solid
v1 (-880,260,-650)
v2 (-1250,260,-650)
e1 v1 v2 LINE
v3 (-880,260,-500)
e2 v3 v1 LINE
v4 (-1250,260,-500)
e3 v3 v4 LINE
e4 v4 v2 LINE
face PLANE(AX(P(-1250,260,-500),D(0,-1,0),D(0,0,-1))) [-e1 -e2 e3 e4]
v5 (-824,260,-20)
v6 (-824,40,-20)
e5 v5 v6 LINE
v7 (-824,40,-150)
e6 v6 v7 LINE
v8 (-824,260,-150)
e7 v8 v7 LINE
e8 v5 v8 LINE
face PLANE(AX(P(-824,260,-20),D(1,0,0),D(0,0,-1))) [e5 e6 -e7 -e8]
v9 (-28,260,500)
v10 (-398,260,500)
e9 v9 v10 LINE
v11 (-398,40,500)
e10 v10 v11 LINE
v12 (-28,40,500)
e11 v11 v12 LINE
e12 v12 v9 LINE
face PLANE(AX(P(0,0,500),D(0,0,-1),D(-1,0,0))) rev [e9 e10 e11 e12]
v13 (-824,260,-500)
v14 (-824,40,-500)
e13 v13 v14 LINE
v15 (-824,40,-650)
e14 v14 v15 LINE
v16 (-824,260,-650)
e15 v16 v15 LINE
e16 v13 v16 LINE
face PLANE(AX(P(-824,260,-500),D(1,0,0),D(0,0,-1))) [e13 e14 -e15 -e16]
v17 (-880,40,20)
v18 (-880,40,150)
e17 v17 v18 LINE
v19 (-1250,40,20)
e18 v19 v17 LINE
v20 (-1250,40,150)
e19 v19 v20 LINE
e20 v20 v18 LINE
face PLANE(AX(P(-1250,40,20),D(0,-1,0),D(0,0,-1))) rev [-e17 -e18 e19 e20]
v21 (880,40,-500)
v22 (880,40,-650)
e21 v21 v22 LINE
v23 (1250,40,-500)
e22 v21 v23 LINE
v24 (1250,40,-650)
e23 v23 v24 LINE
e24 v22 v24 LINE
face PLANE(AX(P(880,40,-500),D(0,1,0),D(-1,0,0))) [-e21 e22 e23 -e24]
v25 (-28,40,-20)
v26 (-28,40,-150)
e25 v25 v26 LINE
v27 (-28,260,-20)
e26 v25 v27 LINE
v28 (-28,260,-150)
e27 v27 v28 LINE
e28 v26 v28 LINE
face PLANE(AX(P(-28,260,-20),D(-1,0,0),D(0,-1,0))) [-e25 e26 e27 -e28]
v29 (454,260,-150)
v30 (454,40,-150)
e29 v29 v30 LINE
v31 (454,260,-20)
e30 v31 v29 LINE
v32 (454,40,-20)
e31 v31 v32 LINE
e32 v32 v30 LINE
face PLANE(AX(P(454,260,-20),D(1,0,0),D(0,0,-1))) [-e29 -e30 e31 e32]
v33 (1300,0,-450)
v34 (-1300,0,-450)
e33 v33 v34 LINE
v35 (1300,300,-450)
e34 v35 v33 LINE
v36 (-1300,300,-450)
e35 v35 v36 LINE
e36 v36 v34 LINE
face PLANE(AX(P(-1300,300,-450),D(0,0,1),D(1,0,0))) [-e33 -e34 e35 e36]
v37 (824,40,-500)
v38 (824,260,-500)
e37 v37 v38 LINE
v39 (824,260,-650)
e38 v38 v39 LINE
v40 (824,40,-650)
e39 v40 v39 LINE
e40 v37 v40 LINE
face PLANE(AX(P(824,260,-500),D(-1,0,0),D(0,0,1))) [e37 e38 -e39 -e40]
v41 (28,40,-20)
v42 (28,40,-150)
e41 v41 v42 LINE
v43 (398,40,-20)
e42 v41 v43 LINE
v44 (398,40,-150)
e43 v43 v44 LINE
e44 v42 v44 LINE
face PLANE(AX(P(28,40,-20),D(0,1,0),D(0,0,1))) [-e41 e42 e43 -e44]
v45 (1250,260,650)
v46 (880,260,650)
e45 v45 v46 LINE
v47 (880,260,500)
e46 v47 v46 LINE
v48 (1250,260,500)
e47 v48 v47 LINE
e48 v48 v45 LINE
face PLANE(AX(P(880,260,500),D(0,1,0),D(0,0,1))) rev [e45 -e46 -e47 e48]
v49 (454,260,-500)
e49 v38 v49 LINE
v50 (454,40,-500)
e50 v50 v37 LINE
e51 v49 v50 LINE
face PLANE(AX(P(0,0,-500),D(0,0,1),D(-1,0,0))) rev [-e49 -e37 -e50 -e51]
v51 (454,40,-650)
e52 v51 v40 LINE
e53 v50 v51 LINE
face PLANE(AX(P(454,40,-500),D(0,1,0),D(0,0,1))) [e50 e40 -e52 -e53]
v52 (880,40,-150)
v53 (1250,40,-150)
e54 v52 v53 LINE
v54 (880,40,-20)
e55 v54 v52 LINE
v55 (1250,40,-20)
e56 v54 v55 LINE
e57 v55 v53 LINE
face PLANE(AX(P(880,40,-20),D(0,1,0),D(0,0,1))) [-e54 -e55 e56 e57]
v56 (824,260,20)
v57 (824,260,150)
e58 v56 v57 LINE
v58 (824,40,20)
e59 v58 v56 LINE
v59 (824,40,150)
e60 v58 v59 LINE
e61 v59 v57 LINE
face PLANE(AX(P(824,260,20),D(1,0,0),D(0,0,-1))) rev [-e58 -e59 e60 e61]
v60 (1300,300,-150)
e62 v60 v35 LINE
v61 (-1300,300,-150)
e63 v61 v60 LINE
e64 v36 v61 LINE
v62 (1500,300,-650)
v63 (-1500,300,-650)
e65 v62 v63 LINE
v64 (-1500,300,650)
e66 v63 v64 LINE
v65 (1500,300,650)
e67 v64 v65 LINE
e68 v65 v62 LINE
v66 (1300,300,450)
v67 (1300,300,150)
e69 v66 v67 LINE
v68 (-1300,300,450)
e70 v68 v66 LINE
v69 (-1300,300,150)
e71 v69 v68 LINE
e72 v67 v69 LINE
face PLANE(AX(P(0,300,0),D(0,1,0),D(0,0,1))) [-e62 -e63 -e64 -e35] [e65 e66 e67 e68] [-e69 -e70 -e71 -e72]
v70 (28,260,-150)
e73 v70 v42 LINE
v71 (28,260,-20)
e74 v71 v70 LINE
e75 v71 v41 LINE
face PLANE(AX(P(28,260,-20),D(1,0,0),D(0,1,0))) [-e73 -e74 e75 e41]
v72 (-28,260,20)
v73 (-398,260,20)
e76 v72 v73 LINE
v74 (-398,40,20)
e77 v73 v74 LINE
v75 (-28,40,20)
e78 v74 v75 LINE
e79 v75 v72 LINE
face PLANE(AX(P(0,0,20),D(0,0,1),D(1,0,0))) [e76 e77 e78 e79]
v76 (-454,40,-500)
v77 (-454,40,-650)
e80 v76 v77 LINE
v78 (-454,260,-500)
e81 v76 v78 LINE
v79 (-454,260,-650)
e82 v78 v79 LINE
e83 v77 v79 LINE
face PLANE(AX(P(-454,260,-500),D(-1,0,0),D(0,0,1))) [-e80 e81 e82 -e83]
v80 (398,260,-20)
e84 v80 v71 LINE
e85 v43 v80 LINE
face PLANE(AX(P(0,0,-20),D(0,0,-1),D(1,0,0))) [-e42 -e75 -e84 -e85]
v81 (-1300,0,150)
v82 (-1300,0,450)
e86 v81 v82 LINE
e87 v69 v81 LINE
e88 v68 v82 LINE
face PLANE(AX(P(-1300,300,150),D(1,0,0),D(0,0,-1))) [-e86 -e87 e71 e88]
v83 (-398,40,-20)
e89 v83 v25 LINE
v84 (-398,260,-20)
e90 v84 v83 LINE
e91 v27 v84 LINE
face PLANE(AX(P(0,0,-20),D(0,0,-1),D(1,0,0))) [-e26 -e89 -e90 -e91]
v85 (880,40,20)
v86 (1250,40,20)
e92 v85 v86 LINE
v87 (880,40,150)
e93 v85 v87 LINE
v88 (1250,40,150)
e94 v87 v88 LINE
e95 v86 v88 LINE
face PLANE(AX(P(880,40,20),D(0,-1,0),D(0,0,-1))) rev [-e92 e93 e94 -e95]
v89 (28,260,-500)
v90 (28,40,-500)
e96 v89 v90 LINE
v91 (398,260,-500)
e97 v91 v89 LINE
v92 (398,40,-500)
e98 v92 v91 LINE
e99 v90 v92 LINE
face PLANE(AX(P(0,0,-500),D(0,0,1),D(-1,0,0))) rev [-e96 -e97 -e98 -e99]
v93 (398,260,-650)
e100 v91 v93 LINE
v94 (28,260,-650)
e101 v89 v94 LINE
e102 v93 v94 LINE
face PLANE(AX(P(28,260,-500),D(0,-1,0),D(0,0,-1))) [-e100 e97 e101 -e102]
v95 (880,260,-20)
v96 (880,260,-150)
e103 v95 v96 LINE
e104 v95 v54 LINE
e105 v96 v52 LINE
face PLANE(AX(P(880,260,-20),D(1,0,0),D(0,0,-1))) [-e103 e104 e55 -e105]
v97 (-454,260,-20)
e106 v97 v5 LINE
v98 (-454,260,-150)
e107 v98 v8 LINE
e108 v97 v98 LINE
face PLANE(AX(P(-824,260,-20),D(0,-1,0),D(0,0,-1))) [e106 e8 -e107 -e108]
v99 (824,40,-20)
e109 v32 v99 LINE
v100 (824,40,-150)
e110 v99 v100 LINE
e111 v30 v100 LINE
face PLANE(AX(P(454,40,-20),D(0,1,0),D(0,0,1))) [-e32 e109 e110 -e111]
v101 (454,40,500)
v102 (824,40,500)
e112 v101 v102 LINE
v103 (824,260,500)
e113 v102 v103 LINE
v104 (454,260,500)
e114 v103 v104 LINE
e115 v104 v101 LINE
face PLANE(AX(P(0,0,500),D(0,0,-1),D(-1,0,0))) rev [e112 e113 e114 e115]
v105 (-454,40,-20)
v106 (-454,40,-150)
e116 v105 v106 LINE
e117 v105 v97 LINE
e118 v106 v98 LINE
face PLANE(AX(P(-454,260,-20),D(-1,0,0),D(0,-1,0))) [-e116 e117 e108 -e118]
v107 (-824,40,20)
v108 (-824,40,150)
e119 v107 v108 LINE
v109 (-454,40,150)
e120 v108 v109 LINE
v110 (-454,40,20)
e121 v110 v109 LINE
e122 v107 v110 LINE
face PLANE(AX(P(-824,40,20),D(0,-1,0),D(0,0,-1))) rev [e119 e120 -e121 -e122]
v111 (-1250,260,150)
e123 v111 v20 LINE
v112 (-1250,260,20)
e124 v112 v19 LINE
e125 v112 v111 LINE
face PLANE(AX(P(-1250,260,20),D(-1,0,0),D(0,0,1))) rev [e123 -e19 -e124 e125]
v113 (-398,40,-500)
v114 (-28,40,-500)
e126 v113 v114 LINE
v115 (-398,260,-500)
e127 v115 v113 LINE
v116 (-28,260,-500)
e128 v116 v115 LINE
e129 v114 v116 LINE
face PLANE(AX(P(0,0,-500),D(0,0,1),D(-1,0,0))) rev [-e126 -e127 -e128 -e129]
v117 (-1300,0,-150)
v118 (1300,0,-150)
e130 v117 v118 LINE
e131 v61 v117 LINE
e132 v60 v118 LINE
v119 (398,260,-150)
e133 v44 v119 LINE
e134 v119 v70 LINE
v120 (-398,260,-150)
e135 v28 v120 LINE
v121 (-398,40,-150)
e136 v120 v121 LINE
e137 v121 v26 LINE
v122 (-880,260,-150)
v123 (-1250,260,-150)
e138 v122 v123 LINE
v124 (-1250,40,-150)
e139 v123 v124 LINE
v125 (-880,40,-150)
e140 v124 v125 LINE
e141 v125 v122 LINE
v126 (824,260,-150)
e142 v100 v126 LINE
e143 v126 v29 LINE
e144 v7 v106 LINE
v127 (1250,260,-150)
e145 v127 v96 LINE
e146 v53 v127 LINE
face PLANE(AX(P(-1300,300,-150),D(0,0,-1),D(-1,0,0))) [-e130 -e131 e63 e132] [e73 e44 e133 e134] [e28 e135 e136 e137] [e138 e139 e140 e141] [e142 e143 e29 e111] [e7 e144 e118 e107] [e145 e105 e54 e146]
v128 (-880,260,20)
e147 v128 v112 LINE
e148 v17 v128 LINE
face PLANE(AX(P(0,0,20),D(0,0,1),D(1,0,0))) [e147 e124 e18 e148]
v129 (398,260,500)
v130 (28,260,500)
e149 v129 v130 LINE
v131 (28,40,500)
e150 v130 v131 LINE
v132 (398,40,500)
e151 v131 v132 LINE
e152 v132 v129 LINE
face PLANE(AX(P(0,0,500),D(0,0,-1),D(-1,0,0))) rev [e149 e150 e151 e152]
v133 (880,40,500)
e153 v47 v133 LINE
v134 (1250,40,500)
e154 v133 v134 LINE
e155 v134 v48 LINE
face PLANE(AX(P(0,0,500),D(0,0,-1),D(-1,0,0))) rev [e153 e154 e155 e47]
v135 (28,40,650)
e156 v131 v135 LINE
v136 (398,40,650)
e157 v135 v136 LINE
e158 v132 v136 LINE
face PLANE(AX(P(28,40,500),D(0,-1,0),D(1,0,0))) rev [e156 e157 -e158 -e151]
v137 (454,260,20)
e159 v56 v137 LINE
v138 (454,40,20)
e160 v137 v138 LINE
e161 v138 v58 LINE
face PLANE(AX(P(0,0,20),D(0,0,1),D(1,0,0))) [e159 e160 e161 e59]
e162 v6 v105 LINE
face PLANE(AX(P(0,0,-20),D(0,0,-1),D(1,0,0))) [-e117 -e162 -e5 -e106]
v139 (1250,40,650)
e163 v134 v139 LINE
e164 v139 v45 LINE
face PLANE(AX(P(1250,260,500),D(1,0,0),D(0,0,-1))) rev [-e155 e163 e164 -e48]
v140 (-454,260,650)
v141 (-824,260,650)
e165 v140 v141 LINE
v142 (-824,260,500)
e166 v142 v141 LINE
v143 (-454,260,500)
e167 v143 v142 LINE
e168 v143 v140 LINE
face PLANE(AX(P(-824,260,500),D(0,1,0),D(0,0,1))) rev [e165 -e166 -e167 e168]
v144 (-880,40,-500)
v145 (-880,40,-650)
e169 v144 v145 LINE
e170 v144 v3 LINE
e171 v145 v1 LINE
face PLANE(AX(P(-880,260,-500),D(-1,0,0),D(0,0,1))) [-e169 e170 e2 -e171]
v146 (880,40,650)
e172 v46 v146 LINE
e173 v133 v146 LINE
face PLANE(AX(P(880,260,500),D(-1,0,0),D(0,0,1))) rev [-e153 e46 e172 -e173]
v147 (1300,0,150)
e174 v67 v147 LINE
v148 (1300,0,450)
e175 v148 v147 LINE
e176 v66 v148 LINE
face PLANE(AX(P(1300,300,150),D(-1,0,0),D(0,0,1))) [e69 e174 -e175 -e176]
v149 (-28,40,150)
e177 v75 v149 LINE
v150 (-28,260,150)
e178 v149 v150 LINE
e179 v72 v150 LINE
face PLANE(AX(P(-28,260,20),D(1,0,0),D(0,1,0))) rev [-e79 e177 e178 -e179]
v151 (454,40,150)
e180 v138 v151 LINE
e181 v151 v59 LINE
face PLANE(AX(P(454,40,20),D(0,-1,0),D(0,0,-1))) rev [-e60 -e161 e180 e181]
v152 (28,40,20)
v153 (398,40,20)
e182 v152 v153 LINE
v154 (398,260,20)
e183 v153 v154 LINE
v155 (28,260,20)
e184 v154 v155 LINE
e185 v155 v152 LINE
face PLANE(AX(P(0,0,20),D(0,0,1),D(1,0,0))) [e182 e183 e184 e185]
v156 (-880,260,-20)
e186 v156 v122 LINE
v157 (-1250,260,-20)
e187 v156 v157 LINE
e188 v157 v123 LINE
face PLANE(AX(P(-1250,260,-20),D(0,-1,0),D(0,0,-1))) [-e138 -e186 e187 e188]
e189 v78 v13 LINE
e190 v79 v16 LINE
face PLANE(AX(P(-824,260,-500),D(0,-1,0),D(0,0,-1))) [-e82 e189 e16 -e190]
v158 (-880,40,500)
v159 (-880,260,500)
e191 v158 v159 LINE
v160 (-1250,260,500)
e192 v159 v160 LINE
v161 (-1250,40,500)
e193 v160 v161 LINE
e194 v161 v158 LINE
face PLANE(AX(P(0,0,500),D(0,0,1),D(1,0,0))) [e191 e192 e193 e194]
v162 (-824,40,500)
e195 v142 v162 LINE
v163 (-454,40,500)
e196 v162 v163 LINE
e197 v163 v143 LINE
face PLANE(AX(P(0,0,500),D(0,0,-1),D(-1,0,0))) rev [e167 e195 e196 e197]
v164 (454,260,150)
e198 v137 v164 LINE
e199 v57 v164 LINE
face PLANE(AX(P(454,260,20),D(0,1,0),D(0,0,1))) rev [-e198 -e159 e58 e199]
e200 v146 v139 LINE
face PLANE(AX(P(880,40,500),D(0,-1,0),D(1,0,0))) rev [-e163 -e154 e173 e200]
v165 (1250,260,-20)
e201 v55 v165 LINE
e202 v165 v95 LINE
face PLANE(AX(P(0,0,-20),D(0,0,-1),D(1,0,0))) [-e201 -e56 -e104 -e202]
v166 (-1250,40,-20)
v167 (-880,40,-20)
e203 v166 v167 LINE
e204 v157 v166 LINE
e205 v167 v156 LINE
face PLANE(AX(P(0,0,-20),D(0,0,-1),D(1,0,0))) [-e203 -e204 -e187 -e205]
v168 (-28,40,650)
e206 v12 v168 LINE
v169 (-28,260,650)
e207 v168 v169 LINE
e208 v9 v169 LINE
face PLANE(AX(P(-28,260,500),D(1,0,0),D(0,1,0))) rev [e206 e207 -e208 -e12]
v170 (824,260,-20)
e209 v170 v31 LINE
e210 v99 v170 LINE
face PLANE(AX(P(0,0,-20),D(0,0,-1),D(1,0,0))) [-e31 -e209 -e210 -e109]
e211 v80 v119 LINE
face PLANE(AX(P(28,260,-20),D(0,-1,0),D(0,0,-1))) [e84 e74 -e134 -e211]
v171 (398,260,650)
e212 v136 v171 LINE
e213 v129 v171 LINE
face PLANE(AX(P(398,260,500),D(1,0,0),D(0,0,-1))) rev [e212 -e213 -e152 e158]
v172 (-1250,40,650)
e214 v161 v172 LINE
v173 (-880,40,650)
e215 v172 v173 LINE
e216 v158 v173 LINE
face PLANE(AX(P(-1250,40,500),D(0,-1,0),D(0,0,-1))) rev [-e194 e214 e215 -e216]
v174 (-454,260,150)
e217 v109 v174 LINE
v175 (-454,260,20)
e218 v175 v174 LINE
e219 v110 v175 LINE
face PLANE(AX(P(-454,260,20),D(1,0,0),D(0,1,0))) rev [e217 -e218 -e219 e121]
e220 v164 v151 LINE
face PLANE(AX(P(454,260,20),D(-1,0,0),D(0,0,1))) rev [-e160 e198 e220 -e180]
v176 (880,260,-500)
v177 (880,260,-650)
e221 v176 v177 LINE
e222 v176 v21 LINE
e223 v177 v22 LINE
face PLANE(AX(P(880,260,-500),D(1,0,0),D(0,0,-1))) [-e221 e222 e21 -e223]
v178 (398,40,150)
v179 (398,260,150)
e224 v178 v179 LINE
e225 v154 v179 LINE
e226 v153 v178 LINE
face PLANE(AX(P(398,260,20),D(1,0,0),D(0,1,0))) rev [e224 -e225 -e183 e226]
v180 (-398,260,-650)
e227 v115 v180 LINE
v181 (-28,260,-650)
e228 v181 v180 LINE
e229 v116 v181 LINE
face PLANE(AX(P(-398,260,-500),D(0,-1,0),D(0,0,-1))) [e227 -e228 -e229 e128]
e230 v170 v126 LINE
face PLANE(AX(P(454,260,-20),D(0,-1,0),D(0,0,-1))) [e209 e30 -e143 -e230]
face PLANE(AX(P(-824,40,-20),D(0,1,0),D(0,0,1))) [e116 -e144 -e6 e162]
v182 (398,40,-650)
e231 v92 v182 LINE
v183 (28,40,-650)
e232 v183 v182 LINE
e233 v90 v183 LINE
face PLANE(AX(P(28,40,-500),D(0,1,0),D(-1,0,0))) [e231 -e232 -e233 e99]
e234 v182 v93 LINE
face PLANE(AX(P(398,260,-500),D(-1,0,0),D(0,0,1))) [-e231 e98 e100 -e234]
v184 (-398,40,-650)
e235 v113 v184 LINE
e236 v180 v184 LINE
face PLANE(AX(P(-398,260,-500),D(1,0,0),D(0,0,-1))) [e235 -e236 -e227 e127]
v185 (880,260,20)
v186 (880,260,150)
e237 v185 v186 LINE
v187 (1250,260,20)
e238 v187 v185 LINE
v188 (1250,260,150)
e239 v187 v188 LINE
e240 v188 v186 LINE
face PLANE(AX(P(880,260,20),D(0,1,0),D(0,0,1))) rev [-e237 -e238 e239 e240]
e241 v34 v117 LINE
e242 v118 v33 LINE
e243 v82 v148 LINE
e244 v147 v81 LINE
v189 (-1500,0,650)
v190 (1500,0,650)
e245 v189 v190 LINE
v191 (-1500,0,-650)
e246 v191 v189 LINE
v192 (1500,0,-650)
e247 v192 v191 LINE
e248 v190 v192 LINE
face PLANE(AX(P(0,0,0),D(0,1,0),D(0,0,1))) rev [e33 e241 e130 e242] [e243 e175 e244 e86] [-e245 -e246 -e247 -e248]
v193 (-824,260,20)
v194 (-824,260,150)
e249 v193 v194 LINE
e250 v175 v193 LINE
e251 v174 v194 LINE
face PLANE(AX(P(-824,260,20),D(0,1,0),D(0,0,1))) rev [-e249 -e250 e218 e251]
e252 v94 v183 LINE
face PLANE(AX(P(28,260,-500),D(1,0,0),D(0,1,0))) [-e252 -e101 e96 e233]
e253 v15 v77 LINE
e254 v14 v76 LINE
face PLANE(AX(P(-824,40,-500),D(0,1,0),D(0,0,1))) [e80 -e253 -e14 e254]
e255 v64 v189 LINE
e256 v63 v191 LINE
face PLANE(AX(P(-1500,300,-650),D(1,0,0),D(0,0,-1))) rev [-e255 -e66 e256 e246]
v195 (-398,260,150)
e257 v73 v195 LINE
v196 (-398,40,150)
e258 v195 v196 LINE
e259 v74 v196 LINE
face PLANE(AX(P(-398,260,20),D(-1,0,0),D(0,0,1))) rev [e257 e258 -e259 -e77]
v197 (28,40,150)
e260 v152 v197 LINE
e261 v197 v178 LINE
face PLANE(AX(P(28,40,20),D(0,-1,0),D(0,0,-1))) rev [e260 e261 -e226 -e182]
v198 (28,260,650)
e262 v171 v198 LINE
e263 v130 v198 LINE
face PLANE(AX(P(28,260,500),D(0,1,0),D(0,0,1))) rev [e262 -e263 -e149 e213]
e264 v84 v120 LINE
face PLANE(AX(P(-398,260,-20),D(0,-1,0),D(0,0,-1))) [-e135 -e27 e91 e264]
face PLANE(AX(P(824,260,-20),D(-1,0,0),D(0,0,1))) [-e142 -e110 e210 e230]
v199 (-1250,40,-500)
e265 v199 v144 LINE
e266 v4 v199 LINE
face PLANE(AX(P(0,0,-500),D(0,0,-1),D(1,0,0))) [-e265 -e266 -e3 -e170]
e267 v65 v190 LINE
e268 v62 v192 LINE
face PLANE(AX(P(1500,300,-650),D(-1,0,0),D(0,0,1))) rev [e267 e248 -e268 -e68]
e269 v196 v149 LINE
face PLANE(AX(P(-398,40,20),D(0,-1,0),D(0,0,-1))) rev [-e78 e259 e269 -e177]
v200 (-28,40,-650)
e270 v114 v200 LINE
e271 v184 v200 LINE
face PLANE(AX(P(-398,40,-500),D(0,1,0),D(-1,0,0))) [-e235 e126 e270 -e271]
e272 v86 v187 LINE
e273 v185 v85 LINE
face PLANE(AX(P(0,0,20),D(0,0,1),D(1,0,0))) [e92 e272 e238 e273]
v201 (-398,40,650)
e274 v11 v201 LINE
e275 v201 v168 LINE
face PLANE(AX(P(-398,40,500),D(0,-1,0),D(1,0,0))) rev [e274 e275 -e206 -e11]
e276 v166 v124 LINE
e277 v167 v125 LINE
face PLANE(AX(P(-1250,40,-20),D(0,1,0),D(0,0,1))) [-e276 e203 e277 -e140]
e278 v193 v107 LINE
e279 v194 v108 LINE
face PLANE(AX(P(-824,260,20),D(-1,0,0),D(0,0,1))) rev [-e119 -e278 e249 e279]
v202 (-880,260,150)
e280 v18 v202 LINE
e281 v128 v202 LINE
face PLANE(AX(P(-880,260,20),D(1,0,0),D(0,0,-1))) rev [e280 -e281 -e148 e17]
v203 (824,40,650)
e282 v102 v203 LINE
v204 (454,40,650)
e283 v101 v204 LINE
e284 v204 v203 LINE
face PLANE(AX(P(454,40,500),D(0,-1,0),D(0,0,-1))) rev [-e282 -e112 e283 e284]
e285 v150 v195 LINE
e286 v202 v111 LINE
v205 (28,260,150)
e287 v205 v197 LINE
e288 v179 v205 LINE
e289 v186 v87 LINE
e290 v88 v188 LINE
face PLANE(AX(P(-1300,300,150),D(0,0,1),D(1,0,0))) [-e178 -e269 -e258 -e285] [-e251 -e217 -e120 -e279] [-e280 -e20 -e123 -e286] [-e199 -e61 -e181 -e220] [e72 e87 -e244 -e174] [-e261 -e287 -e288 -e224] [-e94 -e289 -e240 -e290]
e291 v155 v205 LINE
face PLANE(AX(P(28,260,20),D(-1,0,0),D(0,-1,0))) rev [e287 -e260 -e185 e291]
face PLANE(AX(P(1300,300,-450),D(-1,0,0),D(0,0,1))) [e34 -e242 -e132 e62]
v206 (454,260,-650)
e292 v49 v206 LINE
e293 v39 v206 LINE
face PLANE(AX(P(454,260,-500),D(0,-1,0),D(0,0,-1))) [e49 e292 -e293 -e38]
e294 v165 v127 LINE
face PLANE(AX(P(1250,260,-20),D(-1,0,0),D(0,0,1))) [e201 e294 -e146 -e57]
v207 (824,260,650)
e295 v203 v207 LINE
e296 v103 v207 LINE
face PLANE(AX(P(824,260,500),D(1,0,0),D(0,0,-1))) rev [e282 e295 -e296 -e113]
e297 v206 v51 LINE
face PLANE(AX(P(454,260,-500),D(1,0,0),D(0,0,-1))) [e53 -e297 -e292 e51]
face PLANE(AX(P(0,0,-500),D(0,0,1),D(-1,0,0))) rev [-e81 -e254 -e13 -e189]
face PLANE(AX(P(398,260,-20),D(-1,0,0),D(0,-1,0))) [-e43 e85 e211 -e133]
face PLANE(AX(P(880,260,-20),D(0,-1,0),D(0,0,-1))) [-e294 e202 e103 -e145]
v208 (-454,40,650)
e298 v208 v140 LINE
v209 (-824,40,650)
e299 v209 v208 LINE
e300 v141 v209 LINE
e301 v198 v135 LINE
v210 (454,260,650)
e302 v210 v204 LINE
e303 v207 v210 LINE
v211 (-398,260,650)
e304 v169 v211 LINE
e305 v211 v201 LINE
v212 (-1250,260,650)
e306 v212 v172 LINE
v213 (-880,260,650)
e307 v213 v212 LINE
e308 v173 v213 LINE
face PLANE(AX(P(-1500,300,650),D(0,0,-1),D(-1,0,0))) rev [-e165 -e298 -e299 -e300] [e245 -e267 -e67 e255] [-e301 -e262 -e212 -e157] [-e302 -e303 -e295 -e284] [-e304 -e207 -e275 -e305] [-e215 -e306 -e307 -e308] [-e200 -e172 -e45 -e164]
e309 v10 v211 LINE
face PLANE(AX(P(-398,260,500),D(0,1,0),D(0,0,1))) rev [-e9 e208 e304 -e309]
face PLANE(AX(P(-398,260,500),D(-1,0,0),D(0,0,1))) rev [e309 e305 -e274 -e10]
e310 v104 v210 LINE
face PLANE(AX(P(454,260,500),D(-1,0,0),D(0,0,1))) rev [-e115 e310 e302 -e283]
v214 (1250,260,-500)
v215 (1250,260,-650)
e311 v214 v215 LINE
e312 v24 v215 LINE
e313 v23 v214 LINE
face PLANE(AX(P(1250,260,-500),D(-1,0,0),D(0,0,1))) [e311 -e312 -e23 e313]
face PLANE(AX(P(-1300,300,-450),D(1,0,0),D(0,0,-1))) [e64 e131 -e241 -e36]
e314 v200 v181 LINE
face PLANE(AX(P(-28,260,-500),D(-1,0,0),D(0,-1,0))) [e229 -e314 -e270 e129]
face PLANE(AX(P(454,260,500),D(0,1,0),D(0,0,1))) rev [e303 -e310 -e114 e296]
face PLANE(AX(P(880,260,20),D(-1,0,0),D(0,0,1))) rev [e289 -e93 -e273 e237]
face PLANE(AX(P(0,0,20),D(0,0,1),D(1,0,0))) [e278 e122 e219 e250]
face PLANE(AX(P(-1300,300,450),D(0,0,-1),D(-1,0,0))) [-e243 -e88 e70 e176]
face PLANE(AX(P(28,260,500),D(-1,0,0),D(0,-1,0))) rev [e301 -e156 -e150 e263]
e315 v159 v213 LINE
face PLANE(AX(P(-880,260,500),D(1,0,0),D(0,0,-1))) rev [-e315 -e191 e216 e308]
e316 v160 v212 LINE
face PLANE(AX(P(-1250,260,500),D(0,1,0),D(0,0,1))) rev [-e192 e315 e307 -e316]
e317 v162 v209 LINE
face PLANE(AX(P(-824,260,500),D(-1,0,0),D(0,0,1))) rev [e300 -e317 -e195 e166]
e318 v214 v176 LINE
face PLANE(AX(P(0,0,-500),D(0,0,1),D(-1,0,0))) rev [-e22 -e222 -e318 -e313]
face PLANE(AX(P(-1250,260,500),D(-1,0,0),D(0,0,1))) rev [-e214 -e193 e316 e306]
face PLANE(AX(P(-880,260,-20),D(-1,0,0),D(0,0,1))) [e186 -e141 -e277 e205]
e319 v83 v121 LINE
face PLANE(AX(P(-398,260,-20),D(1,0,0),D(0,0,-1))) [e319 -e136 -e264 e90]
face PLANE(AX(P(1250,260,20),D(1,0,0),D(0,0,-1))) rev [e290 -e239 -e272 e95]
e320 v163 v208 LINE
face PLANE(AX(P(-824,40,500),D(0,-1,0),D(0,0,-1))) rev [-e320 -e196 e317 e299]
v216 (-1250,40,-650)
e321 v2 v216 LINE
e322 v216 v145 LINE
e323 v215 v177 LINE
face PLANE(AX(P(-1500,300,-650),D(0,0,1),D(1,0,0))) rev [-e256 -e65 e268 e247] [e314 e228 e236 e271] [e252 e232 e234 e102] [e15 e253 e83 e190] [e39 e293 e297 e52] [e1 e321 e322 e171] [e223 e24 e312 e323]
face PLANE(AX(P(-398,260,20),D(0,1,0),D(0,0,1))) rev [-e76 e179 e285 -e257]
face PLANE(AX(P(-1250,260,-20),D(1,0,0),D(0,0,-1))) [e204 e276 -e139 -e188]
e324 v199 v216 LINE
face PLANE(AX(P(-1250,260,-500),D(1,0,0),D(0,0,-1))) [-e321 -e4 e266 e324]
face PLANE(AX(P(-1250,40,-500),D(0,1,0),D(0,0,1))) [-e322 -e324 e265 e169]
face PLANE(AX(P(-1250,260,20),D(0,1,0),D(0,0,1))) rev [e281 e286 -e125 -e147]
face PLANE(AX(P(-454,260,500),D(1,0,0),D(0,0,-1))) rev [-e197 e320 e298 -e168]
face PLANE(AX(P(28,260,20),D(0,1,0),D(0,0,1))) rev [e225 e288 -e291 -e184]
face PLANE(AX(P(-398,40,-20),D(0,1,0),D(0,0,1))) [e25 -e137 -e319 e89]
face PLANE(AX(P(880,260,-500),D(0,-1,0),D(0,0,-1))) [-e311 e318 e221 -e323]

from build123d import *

# Parameters (mm, degrees)
SKETCH1_W           = 3000
SKETCH1_H           = 1300
SKETCH1_W_2         = 2600
SKETCH1_H_2         = 300
BOSS_EXTRUDE1_DEPTH = 300
SKETCH2_W           = 370
SKETCH2_H           = 220
CUT_EXTRUDE1_DEPTH  = 150
SKETCH3_W           = 370
SKETCH3_H           = 220
CUT_EXTRUDE2_DEPTH  = 130


with BuildPart() as part:
    # Sketch1 → Boss-Extrude1 (new body)
    with BuildSketch(Plane(origin=(0, 0, 0), x_dir=(1, 0, 0), z_dir=(0, 1, 0))):
        Rectangle(SKETCH1_W, SKETCH1_H)
        with Locations((0, 300)):
            Rectangle(SKETCH1_W_2, SKETCH1_H_2, mode=Mode.SUBTRACT)
        with Locations((0, -300)):
            Rectangle(SKETCH1_W_2, SKETCH1_H_2, mode=Mode.SUBTRACT)
    extrude(amount=BOSS_EXTRUDE1_DEPTH)

    # Sketch2 → Cut-Extrude1 (cut)
    with BuildSketch(Plane.XY.offset(650)):
        with Locations((-1065, 150)):
            Rectangle(SKETCH2_W, SKETCH2_H)
        with Locations((1065, 150)):
            Rectangle(SKETCH2_W, SKETCH2_H)
        with Locations((-639, 150)):
            Rectangle(SKETCH2_W, SKETCH2_H)
        with Locations((-213, 150)):
            Rectangle(SKETCH2_W, SKETCH2_H)
        with Locations((213, 150)):
            Rectangle(SKETCH2_W, SKETCH2_H)
        with Locations((639, 150)):
            Rectangle(SKETCH2_W, SKETCH2_H)
    cut_extrude1 = extrude(amount=-CUT_EXTRUDE1_DEPTH, mode=Mode.SUBTRACT)

    # Mirror1: Cut-Extrude1 across plane
    add(cut_extrude1.mirror(Plane.XY), mode=Mode.SUBTRACT)

    # Sketch3 → Cut-Extrude2 (cut)
    with BuildSketch(Plane.XY.offset(150)):
        with Locations((-1065, 150)):
            Rectangle(SKETCH3_W, SKETCH3_H)
        with Locations((-639, 150)):
            Rectangle(SKETCH3_W, SKETCH3_H)
        with Locations((-213, 150)):
            Rectangle(SKETCH3_W, SKETCH3_H)
        with Locations((213, 150)):
            Rectangle(SKETCH3_W, SKETCH3_H)
        with Locations((639, 150)):
            Rectangle(SKETCH3_W, SKETCH3_H)
        with Locations((1065, 150)):
            Rectangle(SKETCH3_W, SKETCH3_H)
    cut_extrude2 = extrude(amount=-CUT_EXTRUDE2_DEPTH, mode=Mode.SUBTRACT)

    # Mirror2: Cut-Extrude2 across plane
    add(cut_extrude2.mirror(Plane.XY), mode=Mode.SUBTRACT)


solid = part.part
